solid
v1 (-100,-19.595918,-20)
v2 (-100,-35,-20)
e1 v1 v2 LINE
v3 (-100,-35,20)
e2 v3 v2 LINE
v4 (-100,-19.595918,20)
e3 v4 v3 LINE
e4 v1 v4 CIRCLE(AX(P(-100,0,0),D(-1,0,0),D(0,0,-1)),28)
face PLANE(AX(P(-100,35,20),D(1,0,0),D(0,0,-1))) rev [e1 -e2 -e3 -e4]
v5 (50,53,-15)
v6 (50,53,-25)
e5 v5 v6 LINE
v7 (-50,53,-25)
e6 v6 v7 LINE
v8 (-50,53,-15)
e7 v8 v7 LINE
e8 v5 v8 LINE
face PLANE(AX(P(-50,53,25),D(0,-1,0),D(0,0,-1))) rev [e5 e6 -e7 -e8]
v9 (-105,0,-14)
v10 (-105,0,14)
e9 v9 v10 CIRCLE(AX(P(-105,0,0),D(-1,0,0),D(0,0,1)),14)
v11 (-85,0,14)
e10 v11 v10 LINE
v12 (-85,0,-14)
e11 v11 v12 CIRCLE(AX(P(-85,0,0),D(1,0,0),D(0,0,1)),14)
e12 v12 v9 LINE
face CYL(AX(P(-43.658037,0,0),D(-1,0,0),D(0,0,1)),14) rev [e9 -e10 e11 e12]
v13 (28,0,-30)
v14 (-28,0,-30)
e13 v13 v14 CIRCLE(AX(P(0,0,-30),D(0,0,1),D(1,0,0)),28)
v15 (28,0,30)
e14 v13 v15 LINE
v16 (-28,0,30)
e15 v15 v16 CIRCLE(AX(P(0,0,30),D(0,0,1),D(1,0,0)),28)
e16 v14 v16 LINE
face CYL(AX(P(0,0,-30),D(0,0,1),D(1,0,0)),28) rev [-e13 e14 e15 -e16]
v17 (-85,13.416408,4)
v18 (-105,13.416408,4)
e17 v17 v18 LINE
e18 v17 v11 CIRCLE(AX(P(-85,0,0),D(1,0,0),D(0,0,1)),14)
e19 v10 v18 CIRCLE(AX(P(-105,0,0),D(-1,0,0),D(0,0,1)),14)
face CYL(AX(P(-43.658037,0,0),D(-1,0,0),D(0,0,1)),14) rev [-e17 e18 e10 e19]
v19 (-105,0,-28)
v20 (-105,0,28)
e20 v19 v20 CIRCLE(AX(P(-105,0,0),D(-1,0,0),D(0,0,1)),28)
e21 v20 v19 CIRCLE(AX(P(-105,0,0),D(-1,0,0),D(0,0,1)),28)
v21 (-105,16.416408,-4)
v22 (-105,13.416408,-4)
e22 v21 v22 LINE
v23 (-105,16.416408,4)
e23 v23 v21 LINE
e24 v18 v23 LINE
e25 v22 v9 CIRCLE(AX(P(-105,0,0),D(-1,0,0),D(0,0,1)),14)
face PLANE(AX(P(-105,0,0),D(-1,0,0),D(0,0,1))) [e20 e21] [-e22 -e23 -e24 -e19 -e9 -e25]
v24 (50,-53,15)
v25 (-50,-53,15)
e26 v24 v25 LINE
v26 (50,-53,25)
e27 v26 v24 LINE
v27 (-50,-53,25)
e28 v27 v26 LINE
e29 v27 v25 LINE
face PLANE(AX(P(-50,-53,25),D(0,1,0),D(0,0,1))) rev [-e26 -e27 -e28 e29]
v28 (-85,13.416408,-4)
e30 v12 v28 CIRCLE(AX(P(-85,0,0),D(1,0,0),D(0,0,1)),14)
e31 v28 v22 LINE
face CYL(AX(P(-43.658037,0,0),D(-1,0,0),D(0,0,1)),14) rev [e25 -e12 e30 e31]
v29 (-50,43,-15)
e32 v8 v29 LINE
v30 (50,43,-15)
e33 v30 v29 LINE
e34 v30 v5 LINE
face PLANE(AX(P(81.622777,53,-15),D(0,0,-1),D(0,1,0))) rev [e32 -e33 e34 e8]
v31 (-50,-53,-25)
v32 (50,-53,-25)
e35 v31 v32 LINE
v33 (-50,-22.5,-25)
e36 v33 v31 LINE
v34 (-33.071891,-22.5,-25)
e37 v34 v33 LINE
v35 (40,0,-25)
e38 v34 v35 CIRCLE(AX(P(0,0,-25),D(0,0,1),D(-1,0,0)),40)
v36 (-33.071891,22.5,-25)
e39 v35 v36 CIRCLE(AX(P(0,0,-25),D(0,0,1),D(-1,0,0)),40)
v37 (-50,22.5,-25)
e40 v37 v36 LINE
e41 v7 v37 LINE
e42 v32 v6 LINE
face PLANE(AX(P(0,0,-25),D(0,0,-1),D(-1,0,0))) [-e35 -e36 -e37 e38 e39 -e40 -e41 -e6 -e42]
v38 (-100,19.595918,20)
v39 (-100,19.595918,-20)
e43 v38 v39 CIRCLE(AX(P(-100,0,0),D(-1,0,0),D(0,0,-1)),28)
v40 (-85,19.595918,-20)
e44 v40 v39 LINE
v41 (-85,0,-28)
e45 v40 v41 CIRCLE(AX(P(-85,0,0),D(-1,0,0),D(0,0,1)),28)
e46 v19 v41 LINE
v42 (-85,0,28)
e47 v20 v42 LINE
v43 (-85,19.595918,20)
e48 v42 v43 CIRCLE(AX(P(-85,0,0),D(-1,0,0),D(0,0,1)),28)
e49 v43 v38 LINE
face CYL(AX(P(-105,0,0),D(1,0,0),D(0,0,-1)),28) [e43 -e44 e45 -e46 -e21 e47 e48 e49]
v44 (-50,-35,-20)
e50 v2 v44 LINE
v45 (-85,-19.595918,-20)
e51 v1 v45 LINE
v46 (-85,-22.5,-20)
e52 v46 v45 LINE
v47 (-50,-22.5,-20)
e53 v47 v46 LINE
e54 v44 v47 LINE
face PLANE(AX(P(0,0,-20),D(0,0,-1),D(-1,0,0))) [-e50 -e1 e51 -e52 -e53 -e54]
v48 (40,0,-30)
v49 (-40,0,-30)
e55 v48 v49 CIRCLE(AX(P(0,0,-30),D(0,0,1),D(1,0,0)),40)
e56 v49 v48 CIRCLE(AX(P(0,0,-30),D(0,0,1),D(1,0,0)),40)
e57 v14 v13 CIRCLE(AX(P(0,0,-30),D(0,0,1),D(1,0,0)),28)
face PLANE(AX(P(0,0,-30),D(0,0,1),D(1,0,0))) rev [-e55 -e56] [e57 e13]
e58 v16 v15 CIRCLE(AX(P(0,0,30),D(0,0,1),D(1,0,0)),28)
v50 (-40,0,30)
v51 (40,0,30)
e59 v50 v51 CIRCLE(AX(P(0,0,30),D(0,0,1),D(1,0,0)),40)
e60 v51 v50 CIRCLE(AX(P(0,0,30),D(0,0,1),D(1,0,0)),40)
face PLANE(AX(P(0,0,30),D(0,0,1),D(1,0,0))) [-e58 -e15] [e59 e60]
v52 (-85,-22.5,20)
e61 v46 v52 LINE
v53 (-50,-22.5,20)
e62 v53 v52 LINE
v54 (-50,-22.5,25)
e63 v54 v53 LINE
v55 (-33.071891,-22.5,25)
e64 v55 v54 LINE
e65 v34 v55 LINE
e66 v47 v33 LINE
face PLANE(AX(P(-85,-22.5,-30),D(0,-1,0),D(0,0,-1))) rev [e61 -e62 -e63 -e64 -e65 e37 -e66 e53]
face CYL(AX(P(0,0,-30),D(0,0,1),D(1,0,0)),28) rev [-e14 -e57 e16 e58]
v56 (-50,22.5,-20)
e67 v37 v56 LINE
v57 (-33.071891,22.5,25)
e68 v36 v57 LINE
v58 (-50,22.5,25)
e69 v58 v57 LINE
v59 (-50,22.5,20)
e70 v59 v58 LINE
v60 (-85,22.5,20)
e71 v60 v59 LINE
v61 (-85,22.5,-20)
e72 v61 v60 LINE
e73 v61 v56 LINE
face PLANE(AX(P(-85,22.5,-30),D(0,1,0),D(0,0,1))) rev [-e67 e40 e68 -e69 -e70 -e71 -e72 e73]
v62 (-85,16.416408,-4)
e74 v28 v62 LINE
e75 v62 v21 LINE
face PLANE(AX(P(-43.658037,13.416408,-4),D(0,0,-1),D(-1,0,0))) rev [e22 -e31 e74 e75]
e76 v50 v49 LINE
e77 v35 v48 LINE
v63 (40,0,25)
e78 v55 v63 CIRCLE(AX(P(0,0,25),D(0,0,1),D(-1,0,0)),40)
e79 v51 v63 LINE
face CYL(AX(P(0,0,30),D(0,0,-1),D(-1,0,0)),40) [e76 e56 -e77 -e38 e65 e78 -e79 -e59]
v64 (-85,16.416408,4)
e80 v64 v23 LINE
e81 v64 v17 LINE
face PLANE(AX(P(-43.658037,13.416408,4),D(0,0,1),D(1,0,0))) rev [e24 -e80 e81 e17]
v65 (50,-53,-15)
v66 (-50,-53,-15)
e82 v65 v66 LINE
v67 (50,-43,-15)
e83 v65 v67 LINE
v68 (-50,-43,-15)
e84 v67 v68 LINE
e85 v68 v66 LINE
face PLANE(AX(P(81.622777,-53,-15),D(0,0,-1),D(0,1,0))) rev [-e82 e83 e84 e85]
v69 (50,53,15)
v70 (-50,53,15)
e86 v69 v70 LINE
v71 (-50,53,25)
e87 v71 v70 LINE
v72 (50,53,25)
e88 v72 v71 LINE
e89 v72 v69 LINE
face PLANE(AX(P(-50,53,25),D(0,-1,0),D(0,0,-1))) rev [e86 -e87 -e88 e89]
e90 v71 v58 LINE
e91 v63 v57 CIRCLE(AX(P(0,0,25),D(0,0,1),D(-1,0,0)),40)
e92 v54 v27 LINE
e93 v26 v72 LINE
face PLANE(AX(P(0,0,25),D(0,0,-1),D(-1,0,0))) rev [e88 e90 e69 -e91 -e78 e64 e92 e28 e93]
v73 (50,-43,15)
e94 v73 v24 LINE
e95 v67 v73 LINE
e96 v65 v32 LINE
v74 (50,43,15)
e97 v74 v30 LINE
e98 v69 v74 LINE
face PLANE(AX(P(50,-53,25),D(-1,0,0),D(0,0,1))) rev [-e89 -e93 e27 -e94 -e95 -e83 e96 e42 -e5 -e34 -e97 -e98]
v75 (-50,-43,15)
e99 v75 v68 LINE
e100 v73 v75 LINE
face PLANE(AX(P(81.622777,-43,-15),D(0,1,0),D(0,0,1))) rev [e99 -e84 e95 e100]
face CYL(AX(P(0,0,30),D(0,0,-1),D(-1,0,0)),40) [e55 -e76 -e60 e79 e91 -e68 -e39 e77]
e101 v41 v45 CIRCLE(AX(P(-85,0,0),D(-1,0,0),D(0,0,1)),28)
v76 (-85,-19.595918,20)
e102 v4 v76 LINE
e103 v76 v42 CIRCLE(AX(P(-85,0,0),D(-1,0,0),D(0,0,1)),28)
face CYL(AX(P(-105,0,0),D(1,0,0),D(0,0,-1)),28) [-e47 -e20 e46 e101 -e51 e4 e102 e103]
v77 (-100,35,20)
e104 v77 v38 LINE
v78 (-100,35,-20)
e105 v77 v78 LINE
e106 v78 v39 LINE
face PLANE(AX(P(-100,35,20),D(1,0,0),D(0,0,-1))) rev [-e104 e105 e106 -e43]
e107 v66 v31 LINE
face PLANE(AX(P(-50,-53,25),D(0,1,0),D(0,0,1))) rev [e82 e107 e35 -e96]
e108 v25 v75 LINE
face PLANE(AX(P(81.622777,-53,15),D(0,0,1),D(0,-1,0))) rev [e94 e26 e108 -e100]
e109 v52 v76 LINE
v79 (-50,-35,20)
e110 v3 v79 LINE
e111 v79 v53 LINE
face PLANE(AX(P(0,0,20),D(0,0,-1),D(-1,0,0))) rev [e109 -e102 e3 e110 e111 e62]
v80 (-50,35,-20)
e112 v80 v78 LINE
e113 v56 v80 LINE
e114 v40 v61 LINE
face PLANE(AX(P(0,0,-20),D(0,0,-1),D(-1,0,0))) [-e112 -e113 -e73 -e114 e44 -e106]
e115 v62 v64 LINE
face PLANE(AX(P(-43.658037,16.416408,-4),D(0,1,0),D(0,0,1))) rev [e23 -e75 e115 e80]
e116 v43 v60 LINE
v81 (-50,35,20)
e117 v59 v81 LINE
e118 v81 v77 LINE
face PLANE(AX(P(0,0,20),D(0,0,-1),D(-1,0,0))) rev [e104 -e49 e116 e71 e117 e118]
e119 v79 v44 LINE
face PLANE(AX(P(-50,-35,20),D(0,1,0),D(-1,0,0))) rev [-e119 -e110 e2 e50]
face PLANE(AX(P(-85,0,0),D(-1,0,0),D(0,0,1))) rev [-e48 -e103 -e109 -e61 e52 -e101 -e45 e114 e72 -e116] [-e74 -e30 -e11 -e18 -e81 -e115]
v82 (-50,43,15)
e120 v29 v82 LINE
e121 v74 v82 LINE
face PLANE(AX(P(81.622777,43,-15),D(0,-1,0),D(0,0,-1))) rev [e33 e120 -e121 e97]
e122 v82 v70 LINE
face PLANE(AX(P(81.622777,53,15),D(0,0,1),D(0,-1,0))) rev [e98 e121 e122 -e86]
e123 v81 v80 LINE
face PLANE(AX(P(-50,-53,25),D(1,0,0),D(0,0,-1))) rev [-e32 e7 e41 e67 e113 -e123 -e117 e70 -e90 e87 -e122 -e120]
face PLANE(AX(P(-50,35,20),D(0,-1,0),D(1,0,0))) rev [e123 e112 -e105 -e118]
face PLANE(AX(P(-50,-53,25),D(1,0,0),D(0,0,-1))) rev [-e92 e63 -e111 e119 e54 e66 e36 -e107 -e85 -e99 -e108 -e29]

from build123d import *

# Parameters (mm, degrees)
BASE_BLOCK_PROFILE_W         = 100
BASE_BLOCK_PROFILE_H         = 106
BASE_BLOCK_DEPTH             = 25
HOUSING_BOSS_PROFILE_W       = 50
HOUSING_BOSS_PROFILE_H       = 70
HOUSING_BOSS_DEPTH           = 20
GUIDE_KEY_SLOTS_PROFILE_W    = 30
GUIDE_KEY_SLOTS_PROFILE_H    = 10
GUIDE_KEY_SLOTS_DEPTH        = 100
BEARING_BOSS_PROFILE_80_R    = 40
BEARING_BOSS_80_DEPTH        = 30
BEARING_COLLAR_56_DEPTH      = 5
BEARING_COLLAR_56_DEPTH_BACK = 15
BEARING_COLLAR_PROFILE_56_R  = 28
BEARING_BORE_DEPTH           = 122.383689184
BEARING_BORE_DEPTH_BACK      = 122.383689184
BEARING_BORE_PROFILE_R       = 28
BORE_KEYWAY_DEPTH            = 20


with BuildPart() as part:
    # Base Block Profile → Base Block (new, symmetric)
    with BuildSketch(Plane.XY):
        Rectangle(BASE_BLOCK_PROFILE_W, BASE_BLOCK_PROFILE_H)
    extrude(amount=BASE_BLOCK_DEPTH, both=True)

    # Housing Boss Profile → Housing Boss (add, symmetric)
    with BuildSketch(Plane.XY):
        with Locations((-75, 0)):
            Rectangle(HOUSING_BOSS_PROFILE_W, HOUSING_BOSS_PROFILE_H)
    extrude(amount=HOUSING_BOSS_DEPTH, both=True)

    # Guide Key Slots Profile → Guide Key Slots (cut)
    with BuildSketch(Plane.ZY.offset(50)):
        with Locations((0, 48)):
            Rectangle(GUIDE_KEY_SLOTS_PROFILE_W, GUIDE_KEY_SLOTS_PROFILE_H)
        with Locations((0, -48)):
            Rectangle(GUIDE_KEY_SLOTS_PROFILE_W, GUIDE_KEY_SLOTS_PROFILE_H)
    extrude(amount=-GUIDE_KEY_SLOTS_DEPTH, mode=Mode.SUBTRACT)

    # Bearing Boss Profile Ø80 → Bearing Boss Ø80 (add, symmetric)
    with BuildSketch(Plane.XY):
        with Locations(Location((0, 0, 0), (0, 0, 180))):
            Circle(BEARING_BOSS_PROFILE_80_R)
    extrude(amount=BEARING_BOSS_80_DEPTH, both=True)

    # Bearing Collar Profile Ø56 → Bearing Collar Ø56 (add, two sides: drawn at the far end of the back side and taken through both)
    with BuildSketch(Plane.ZY.offset(100).offset(-BEARING_COLLAR_56_DEPTH_BACK)):
        with Locations(Location((0, 0, 0), (0, 0, 224.415308597))):
            Circle(BEARING_COLLAR_PROFILE_56_R)
    extrude(amount=BEARING_COLLAR_56_DEPTH + BEARING_COLLAR_56_DEPTH_BACK)

    # Bearing Bore Profile → Bearing Bore (cut, two sides: drawn at the far end of the back side and taken through both)
    with BuildSketch(Plane.XY.offset(-BEARING_BORE_DEPTH_BACK)):
        Circle(BEARING_BORE_PROFILE_R)
        with BuildLine():
            Line((-85, 22.5), (-33.071891388, 22.5))
            ThreePointArc((-33.071891388, 22.5), (-40, 0), (-33.071891388, -22.5))
            Line((-33.071891388, -22.5), (-85, -22.5))
            Line((-85, -22.5), (-85, 22.5))
        make_face()
    extrude(amount=BEARING_BORE_DEPTH + BEARING_BORE_DEPTH_BACK, mode=Mode.SUBTRACT)

    # Bore Keyway Profile → Bore Keyway (cut)
    with BuildSketch(Plane.ZY.offset(105)):
        with BuildLine():
            Line((-4, 13.416407865), (-4, 16.416407865))
            Line((-4, 16.416407865), (4, 16.416407865))
            Line((4, 16.416407865), (4, 13.416407865))
            ThreePointArc((4, 13.416407865), (0, -14), (-4, 13.416407865))
        make_face()
    extrude(amount=-BORE_KEYWAY_DEPTH, mode=Mode.SUBTRACT)


solid = part.part
